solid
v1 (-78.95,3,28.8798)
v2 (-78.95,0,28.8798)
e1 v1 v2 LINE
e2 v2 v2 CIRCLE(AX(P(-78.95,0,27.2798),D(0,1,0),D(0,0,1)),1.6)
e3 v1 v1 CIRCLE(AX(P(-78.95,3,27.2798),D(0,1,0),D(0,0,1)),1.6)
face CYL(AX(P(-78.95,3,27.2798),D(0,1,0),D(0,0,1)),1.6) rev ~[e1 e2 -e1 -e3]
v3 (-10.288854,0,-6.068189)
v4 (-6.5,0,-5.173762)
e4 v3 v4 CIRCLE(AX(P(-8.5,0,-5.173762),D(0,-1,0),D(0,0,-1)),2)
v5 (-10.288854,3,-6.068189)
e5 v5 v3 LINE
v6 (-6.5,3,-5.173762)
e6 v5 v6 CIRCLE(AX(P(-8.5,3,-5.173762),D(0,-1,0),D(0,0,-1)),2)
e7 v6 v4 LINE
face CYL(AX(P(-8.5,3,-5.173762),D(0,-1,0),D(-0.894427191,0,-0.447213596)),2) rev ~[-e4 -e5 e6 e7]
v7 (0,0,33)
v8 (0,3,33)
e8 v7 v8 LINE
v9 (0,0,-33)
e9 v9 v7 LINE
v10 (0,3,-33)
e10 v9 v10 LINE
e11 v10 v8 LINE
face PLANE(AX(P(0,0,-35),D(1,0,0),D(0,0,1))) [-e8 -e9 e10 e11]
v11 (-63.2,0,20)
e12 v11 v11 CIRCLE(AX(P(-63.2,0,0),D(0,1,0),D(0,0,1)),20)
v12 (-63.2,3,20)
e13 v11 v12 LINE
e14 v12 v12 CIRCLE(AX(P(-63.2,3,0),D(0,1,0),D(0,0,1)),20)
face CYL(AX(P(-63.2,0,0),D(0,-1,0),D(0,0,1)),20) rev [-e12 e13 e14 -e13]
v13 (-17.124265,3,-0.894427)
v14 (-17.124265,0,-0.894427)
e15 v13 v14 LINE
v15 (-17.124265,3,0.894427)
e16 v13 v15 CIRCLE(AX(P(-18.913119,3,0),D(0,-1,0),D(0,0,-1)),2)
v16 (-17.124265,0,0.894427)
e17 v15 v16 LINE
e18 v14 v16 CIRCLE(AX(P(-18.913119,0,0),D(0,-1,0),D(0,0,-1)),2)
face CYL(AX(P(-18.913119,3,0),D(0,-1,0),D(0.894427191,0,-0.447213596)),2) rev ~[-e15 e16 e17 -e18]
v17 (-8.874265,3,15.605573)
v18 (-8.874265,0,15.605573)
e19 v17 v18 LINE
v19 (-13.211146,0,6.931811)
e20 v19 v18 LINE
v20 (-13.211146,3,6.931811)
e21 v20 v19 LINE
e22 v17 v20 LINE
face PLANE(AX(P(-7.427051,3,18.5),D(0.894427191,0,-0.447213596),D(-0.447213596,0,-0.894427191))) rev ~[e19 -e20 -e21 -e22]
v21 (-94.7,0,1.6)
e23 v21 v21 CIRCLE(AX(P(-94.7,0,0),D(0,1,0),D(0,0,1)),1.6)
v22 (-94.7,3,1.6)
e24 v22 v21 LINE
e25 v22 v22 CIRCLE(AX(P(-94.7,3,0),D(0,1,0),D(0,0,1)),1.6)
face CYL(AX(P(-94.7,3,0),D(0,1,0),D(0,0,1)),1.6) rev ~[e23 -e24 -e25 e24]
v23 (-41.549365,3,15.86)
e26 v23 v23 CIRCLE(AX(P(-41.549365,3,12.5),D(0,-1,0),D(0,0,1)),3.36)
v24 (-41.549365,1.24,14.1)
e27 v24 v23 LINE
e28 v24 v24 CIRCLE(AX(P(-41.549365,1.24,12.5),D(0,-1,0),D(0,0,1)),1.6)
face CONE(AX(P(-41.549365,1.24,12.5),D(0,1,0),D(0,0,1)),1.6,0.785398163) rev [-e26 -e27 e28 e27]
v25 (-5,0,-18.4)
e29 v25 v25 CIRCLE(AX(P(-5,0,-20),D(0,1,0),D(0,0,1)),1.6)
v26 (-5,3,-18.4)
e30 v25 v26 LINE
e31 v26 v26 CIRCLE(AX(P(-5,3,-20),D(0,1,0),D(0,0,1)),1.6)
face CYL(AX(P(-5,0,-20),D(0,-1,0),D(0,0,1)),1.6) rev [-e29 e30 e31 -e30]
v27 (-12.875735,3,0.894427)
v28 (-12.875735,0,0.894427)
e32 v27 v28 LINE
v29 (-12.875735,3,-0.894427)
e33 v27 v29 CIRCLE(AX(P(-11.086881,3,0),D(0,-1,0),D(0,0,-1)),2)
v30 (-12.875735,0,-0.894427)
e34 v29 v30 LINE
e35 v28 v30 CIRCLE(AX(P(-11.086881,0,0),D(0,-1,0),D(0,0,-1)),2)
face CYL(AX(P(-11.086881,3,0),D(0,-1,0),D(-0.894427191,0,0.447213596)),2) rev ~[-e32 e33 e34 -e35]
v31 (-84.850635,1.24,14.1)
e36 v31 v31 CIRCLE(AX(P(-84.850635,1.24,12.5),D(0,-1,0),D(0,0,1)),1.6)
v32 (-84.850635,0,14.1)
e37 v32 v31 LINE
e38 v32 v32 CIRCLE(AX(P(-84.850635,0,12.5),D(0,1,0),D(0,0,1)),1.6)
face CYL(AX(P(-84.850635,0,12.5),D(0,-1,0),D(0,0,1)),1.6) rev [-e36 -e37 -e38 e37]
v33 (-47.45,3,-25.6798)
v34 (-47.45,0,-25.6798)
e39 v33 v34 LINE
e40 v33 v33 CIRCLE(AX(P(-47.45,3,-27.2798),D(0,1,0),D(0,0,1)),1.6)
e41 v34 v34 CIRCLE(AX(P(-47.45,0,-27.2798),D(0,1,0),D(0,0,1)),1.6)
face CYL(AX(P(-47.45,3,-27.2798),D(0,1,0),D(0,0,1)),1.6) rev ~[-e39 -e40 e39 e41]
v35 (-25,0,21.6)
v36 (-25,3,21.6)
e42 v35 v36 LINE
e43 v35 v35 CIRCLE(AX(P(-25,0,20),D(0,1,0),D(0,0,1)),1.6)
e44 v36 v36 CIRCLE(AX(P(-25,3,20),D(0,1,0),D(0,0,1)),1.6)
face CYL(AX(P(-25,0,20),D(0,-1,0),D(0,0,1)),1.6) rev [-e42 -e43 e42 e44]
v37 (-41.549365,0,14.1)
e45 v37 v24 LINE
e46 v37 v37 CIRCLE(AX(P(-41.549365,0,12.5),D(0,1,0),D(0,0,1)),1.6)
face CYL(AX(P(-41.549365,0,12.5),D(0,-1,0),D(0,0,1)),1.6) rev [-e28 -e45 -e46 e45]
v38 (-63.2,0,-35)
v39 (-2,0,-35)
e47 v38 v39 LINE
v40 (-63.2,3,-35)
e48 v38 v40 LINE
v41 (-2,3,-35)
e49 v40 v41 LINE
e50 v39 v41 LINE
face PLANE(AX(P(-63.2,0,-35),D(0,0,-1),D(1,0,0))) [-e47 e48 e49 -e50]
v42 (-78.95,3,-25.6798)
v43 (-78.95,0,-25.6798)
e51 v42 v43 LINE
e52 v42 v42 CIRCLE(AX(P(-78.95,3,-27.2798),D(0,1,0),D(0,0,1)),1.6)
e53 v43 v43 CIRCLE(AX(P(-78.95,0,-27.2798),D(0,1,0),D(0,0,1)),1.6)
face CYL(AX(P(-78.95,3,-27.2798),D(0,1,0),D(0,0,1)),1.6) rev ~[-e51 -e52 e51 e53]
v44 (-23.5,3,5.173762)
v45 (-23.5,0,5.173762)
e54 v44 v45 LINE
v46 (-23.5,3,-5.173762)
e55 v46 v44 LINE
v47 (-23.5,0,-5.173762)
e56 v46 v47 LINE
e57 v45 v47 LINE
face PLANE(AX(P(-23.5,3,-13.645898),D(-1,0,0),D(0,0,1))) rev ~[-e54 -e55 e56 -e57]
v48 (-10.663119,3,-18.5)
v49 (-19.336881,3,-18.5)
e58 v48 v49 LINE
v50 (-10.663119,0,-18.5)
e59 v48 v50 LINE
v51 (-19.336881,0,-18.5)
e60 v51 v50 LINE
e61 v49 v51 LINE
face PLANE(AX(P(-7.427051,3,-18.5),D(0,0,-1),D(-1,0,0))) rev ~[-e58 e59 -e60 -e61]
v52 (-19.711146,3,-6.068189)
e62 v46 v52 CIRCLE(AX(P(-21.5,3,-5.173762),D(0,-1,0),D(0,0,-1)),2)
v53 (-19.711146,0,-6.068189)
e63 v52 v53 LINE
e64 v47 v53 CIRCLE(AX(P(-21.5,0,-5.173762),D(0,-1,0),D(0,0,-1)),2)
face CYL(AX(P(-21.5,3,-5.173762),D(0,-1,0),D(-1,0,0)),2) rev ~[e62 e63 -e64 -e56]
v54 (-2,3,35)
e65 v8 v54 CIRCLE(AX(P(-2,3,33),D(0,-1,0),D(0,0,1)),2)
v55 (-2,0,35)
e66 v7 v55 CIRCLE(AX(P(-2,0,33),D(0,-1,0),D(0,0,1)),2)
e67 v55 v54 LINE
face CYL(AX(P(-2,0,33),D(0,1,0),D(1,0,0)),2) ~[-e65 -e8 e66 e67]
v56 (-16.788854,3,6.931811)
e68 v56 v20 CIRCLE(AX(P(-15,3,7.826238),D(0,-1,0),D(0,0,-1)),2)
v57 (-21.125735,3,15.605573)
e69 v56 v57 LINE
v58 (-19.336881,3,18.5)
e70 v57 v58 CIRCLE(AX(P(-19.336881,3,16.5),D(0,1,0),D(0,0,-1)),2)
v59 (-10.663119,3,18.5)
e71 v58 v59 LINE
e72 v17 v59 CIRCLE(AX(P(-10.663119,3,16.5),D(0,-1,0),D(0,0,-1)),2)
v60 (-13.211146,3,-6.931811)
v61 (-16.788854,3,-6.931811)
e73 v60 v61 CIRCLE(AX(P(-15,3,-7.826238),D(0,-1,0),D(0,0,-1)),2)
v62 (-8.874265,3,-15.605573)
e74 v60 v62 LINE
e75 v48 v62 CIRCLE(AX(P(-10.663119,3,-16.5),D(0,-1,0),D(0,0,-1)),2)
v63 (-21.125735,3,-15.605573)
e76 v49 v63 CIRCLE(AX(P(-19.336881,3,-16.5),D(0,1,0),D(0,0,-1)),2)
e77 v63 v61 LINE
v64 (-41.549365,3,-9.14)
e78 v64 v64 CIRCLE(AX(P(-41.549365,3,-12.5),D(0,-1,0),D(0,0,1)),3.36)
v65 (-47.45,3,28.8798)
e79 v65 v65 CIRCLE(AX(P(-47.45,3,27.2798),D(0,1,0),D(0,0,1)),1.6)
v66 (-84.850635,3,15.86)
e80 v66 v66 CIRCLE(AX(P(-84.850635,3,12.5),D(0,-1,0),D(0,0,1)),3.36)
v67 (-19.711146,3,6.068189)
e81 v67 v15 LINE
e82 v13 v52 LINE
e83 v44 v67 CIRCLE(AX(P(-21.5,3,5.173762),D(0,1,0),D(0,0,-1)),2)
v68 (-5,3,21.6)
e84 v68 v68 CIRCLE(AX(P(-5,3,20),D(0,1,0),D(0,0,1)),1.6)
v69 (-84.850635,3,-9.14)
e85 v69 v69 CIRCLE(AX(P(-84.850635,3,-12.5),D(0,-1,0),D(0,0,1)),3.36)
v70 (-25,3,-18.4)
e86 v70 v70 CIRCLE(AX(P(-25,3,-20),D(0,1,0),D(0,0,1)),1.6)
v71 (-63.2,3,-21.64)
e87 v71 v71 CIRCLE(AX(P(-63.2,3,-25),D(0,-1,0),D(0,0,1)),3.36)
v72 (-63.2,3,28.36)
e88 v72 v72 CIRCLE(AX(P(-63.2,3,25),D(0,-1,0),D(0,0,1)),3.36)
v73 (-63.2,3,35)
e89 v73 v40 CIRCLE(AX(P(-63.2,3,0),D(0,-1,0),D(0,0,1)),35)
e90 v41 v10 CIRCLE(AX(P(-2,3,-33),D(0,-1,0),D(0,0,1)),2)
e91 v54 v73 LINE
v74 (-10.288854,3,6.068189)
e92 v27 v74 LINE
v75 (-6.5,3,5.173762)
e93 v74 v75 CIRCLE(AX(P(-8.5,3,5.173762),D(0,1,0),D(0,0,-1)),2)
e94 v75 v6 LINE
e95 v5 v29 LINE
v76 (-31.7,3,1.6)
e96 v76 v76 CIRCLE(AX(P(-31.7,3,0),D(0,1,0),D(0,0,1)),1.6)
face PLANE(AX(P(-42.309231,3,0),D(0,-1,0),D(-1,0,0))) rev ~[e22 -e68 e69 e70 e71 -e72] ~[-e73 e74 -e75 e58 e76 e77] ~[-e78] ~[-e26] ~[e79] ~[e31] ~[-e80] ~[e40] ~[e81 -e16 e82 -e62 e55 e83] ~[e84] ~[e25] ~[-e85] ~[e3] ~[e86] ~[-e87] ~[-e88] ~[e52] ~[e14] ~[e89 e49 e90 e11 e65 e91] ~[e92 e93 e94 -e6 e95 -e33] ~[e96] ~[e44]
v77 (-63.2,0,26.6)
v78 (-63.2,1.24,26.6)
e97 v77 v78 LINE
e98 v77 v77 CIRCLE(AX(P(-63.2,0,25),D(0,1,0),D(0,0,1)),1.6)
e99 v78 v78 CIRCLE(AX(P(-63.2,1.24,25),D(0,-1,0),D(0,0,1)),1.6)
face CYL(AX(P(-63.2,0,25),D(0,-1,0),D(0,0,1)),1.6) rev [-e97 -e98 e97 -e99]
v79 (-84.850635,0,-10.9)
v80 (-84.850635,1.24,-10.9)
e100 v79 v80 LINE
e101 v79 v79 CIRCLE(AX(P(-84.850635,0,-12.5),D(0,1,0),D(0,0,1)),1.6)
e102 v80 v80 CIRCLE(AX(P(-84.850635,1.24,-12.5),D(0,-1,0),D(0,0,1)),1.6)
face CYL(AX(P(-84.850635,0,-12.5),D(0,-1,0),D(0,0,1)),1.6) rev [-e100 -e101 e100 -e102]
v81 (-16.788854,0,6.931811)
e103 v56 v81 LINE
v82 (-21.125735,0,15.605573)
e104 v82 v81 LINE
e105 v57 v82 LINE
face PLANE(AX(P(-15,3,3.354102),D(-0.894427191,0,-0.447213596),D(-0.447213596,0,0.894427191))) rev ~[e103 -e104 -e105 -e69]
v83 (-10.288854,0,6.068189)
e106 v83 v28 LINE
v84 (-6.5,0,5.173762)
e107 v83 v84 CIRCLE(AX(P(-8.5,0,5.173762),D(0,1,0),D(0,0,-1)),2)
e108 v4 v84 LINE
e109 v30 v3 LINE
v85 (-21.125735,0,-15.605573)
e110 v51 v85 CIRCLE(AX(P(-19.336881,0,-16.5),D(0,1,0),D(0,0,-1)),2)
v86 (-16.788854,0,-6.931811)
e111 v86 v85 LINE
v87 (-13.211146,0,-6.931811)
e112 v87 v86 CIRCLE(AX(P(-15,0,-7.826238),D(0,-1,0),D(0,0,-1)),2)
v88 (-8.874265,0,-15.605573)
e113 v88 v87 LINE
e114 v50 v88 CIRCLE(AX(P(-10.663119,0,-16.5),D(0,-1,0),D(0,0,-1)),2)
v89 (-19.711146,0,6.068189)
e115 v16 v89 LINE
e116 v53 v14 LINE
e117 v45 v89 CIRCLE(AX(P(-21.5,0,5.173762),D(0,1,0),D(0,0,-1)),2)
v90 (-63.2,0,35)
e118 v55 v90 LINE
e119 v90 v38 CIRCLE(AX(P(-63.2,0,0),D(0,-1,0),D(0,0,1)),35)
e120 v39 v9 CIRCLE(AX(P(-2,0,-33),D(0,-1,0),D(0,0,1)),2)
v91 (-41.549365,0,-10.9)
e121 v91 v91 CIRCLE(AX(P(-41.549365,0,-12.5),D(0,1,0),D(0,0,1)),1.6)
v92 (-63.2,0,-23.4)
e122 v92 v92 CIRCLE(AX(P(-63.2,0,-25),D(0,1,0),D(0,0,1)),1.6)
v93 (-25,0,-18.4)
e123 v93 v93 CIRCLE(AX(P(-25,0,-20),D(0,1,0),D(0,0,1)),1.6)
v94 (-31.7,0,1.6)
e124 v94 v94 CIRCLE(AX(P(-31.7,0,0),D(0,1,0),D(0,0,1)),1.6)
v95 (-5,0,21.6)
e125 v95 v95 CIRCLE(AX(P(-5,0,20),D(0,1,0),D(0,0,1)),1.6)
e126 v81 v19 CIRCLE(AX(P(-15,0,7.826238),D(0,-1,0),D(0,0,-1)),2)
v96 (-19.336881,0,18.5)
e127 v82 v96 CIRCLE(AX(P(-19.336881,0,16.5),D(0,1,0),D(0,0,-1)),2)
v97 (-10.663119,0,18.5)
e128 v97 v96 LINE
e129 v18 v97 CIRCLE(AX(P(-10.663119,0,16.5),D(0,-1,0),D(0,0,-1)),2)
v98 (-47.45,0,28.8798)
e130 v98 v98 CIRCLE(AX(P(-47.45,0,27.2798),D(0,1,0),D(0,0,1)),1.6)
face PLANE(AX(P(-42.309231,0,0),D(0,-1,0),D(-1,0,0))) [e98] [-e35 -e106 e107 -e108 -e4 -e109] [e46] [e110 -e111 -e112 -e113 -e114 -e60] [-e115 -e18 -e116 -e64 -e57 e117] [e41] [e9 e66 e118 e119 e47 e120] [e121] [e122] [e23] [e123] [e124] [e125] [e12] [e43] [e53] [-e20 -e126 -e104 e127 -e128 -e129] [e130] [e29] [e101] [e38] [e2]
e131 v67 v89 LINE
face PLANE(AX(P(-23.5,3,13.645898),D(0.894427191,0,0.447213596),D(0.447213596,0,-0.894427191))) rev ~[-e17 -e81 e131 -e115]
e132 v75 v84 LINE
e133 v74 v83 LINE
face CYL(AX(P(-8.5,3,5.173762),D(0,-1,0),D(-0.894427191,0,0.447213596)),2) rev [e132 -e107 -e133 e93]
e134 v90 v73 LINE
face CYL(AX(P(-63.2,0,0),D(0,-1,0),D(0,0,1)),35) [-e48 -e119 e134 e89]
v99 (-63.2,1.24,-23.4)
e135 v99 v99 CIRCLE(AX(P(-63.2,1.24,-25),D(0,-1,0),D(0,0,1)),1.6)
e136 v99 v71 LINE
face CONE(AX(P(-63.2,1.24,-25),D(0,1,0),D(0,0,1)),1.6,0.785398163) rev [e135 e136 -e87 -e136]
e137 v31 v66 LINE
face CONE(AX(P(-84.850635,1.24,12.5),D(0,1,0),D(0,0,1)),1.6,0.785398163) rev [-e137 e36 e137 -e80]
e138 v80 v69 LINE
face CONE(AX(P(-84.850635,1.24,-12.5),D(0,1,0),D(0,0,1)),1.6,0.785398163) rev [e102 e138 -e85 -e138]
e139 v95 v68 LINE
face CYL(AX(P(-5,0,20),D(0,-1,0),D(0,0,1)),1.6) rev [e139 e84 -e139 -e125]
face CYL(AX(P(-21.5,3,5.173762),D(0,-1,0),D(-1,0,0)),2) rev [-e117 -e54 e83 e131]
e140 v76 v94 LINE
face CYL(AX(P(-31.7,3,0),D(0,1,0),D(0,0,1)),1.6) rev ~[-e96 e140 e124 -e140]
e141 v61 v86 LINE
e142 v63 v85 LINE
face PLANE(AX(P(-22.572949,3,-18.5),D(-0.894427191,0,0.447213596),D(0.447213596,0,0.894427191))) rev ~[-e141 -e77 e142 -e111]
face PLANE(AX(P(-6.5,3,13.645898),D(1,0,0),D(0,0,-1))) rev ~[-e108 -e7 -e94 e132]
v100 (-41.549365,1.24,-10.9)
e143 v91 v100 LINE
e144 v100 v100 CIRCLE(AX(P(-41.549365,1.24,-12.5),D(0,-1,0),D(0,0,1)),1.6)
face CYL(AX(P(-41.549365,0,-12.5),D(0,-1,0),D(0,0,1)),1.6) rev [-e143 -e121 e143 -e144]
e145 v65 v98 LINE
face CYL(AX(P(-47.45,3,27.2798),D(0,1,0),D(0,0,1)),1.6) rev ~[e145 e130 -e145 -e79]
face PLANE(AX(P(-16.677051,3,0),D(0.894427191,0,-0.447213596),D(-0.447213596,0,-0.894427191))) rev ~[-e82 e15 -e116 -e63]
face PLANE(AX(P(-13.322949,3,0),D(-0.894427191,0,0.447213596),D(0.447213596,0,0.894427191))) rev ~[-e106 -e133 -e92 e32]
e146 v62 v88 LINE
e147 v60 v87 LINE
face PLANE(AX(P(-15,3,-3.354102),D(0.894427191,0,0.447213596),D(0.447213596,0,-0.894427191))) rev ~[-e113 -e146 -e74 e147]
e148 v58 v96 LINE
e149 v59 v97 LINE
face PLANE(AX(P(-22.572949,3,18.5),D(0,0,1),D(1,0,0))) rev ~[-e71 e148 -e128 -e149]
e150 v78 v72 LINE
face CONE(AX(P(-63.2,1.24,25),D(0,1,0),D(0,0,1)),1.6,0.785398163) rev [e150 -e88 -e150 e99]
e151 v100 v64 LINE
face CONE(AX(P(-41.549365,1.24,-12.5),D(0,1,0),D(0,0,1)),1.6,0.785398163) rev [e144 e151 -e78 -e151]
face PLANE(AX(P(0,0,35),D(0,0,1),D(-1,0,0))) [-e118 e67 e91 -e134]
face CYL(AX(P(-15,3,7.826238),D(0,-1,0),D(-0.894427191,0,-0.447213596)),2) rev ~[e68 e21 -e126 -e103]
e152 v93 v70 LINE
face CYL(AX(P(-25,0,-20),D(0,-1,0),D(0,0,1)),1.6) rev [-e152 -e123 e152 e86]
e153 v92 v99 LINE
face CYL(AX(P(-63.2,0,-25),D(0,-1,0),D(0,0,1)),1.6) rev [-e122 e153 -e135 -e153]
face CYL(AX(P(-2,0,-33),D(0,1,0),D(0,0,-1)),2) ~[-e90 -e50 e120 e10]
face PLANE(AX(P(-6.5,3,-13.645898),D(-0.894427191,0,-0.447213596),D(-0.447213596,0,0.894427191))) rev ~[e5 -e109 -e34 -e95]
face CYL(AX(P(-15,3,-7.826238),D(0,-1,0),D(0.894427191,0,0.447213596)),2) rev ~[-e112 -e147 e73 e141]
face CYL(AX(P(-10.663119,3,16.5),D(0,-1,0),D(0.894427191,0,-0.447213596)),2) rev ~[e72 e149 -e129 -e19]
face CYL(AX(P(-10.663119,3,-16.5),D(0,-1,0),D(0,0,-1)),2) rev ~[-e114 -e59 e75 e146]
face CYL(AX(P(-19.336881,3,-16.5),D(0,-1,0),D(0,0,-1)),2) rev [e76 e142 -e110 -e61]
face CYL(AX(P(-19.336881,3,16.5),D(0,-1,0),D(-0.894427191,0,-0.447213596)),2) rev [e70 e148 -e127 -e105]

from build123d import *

# Parameters (mm, degrees)
SKETCH_1_R                  = 1.6
SKETCH_1_R_2                = 20
EXTRUDE_1_DEPTH             = 3
HOLE_WIZARD_M3_1_AT_2_COUNT = 2
HOLE_WIZARD_M3_1_AT_2_PITCH = 25
HOLE_WIZARD_M3_1_AT_3_COUNT = 2
HOLE_WIZARD_M3_1_AT_3_PITCH = 43.301270189
HOLE_WIZARD_M3_1_AT_4_COUNT = 2
HOLE_WIZARD_M3_1_AT_4_PITCH = 50
HOLE_WIZARD_M3_1_AT_5_COUNT = 2
HOLE_WIZARD_M3_1_AT_5_PITCH = 43.301270189
HOLE_WIZARD_M3_1_AT_6_COUNT = 2
HOLE_WIZARD_M3_1_AT_6_PITCH = 25
SKETCH_3_R                  = 1.6
CUT_EXTRUDE_1_DEPTH         = 10
CUT_EXTRUDE_2_DEPTH         = 10
FILLET_1_R                  = 2


with BuildPart() as part:
    # 草图1 → 凸台-拉伸1 (new body)
    with BuildSketch(Plane(origin=(0, 0, 0), x_dir=(1, 0, 0), z_dir=(0, 1, 0))):
        with BuildLine():
            Line((-63.2, 35), (0, 35))
            Line((0, 35), (0, -35))
            Line((0, -35), (-63.2, -35))
            ThreePointArc((-63.2, -35), (-98.2, 0), (-63.2, 35))
        make_face()
        with Locations(Location((-63.2, 25, 0), (0, 0, 270))):
            Circle(SKETCH_1_R, mode=Mode.SUBTRACT)
        with Locations(Location((-41.549364905, 12.5, 0), (0, 0, 270))):
            Circle(SKETCH_1_R, mode=Mode.SUBTRACT)
        with Locations(Location((-41.549364905, -12.5, 0), (0, 0, 270))):
            Circle(SKETCH_1_R, mode=Mode.SUBTRACT)
        with Locations(Location((-63.2, -25, 0), (0, 0, 270))):
            Circle(SKETCH_1_R, mode=Mode.SUBTRACT)
        with Locations(Location((-84.850635095, -12.5, 0), (0, 0, 270))):
            Circle(SKETCH_1_R, mode=Mode.SUBTRACT)
        with Locations(Location((-84.850635095, 12.5, 0), (0, 0, 270))):
            Circle(SKETCH_1_R, mode=Mode.SUBTRACT)
        with Locations(Location((-63.2, 0, 0), (0, 0, 270))):
            Circle(SKETCH_1_R_2, mode=Mode.SUBTRACT)
        with Locations(Location((-25, 20, 0), (0, 0, 270))):
            Circle(SKETCH_1_R, mode=Mode.SUBTRACT)
        with Locations(Location((-5, 20, 0), (0, 0, 270))):
            Circle(SKETCH_1_R, mode=Mode.SUBTRACT)
        with Locations(Location((-5, -20, 0), (0, 0, 270))):
            Circle(SKETCH_1_R, mode=Mode.SUBTRACT)
        with Locations(Location((-25, -20, 0), (0, 0, 270))):
            Circle(SKETCH_1_R, mode=Mode.SUBTRACT)
    extrude(amount=EXTRUDE_1_DEPTH)

    # 草图2 → M3 六角凹锥坑螺钉的锥形沉头孔1 (revolve, cut)
    with BuildSketch(Plane(origin=(-63.2, 3, -25), x_dir=(0, 0, 1), z_dir=(1, 0, 0))):
        Polygon((0, 0), (0, 3), (1.6, 3), (1.6, 1.76), (3.36, 0), align=None)
    hole_wizard_m3_1 = revolve(axis=Axis((-63.2, 9.35, -25), (0, -1, 0)), mode=Mode.SUBTRACT)

    # M3 六角凹锥坑螺钉的锥形沉头孔1 at 2: M3 六角凹锥坑螺钉的锥形沉头孔1 ×2
    with Locations(*[Vector(0.8660254037844387, 0, 0.5) * (i * HOLE_WIZARD_M3_1_AT_2_PITCH) for i in range(1, HOLE_WIZARD_M3_1_AT_2_COUNT)]):
        add(hole_wizard_m3_1, mode=Mode.SUBTRACT)

    # M3 六角凹锥坑螺钉的锥形沉头孔1 at 3: M3 六角凹锥坑螺钉的锥形沉头孔1 ×2
    with Locations(*[Vector(0.5000000000000001, 0, 0.8660254037844386) * (i * HOLE_WIZARD_M3_1_AT_3_PITCH) for i in range(1, HOLE_WIZARD_M3_1_AT_3_COUNT)]):
        add(hole_wizard_m3_1, mode=Mode.SUBTRACT)

    # M3 六角凹锥坑螺钉的锥形沉头孔1 at 4: M3 六角凹锥坑螺钉的锥形沉头孔1 ×2
    with Locations(*[(0, 0, i * HOLE_WIZARD_M3_1_AT_4_PITCH) for i in range(1, HOLE_WIZARD_M3_1_AT_4_COUNT)]):
        add(hole_wizard_m3_1, mode=Mode.SUBTRACT)

    # M3 六角凹锥坑螺钉的锥形沉头孔1 at 5: M3 六角凹锥坑螺钉的锥形沉头孔1 ×2
    with Locations(*[Vector(-0.49999999999999983, 0, 0.8660254037844388) * (i * HOLE_WIZARD_M3_1_AT_5_PITCH) for i in range(1, HOLE_WIZARD_M3_1_AT_5_COUNT)]):
        add(hole_wizard_m3_1, mode=Mode.SUBTRACT)

    # M3 六角凹锥坑螺钉的锥形沉头孔1 at 6: M3 六角凹锥坑螺钉的锥形沉头孔1 ×2
    with Locations(*[Vector(-0.8660254037844388, 0, 0.4999999999999997) * (i * HOLE_WIZARD_M3_1_AT_6_PITCH) for i in range(1, HOLE_WIZARD_M3_1_AT_6_COUNT)]):
        add(hole_wizard_m3_1, mode=Mode.SUBTRACT)

    # 草图3 → 切除-拉伸1 (cut)
    with BuildSketch(Plane(origin=(0, 3, 0), x_dir=(1, 0, 0), z_dir=(0, 1, 0))):
        with Locations(Location((-31.7, 0, 0), (0, 0, 270))):
            Circle(SKETCH_3_R)
        with Locations(Location((-47.45, -27.279800219, 0), (0, 0, 270))):
            Circle(SKETCH_3_R)
        with Locations(Location((-78.95, -27.279800219, 0), (0, 0, 270))):
            Circle(SKETCH_3_R)
        with Locations(Location((-94.7, 0, 0), (0, 0, 270))):
            Circle(SKETCH_3_R)
        with Locations(Location((-78.95, 27.279800219, 0), (0, 0, 270))):
            Circle(SKETCH_3_R)
        with Locations(Location((-47.45, 27.279800219, 0), (0, 0, 270))):
            Circle(SKETCH_3_R)
    extrude(amount=-CUT_EXTRUDE_1_DEPTH, mode=Mode.SUBTRACT)

    # 草图4 → 切除-拉伸2 (cut)
    with BuildSketch(Plane(origin=(0, 3, 0), x_dir=(1, 0, 0), z_dir=(0, 1, 0))):
        Polygon((-23.5, 13.645898034), (-23.5, -13.645898034), (-16.677050983, 0), align=None)
        Polygon((-15, -3.354101966), (-22.572949017, -18.5), (-7.427050983, -18.5), align=None)
        Polygon((-7.427050983, 18.5), (-22.572949017, 18.5), (-15, 3.354101966), align=None)
        Polygon((-13.322949017, 0), (-6.5, -13.645898034), (-6.5, 13.645898034), align=None)
    extrude(amount=-CUT_EXTRUDE_2_DEPTH, mode=Mode.SUBTRACT)

    # 圆角1
    fillet_1_edges = [part.edges().sort_by_distance(p)[0] for p in [
        (-22.572949017, 1.5, 18.5),
        (-15, 1.5, 3.354101966),
        (-7.427050983, 1.5, 18.5),
        (-22.572949017, 1.5, -18.5),
        (-7.427050983, 1.5, -18.5),
        (-15, 1.5, -3.354101966),
        (-13.322949017, 1.5, 0),
        (-6.5, 1.5, -13.645898034),
        (-6.5, 1.5, 13.645898034),
        (-23.5, 1.5, 13.645898034),
        (-23.5, 1.5, -13.645898034),
        (-16.677050983, 1.5, 0),
        (0, 1.5, -35),
        (0, 1.5, 35),
    ]]
    fillet(fillet_1_edges, radius=FILLET_1_R)


solid = part.part
